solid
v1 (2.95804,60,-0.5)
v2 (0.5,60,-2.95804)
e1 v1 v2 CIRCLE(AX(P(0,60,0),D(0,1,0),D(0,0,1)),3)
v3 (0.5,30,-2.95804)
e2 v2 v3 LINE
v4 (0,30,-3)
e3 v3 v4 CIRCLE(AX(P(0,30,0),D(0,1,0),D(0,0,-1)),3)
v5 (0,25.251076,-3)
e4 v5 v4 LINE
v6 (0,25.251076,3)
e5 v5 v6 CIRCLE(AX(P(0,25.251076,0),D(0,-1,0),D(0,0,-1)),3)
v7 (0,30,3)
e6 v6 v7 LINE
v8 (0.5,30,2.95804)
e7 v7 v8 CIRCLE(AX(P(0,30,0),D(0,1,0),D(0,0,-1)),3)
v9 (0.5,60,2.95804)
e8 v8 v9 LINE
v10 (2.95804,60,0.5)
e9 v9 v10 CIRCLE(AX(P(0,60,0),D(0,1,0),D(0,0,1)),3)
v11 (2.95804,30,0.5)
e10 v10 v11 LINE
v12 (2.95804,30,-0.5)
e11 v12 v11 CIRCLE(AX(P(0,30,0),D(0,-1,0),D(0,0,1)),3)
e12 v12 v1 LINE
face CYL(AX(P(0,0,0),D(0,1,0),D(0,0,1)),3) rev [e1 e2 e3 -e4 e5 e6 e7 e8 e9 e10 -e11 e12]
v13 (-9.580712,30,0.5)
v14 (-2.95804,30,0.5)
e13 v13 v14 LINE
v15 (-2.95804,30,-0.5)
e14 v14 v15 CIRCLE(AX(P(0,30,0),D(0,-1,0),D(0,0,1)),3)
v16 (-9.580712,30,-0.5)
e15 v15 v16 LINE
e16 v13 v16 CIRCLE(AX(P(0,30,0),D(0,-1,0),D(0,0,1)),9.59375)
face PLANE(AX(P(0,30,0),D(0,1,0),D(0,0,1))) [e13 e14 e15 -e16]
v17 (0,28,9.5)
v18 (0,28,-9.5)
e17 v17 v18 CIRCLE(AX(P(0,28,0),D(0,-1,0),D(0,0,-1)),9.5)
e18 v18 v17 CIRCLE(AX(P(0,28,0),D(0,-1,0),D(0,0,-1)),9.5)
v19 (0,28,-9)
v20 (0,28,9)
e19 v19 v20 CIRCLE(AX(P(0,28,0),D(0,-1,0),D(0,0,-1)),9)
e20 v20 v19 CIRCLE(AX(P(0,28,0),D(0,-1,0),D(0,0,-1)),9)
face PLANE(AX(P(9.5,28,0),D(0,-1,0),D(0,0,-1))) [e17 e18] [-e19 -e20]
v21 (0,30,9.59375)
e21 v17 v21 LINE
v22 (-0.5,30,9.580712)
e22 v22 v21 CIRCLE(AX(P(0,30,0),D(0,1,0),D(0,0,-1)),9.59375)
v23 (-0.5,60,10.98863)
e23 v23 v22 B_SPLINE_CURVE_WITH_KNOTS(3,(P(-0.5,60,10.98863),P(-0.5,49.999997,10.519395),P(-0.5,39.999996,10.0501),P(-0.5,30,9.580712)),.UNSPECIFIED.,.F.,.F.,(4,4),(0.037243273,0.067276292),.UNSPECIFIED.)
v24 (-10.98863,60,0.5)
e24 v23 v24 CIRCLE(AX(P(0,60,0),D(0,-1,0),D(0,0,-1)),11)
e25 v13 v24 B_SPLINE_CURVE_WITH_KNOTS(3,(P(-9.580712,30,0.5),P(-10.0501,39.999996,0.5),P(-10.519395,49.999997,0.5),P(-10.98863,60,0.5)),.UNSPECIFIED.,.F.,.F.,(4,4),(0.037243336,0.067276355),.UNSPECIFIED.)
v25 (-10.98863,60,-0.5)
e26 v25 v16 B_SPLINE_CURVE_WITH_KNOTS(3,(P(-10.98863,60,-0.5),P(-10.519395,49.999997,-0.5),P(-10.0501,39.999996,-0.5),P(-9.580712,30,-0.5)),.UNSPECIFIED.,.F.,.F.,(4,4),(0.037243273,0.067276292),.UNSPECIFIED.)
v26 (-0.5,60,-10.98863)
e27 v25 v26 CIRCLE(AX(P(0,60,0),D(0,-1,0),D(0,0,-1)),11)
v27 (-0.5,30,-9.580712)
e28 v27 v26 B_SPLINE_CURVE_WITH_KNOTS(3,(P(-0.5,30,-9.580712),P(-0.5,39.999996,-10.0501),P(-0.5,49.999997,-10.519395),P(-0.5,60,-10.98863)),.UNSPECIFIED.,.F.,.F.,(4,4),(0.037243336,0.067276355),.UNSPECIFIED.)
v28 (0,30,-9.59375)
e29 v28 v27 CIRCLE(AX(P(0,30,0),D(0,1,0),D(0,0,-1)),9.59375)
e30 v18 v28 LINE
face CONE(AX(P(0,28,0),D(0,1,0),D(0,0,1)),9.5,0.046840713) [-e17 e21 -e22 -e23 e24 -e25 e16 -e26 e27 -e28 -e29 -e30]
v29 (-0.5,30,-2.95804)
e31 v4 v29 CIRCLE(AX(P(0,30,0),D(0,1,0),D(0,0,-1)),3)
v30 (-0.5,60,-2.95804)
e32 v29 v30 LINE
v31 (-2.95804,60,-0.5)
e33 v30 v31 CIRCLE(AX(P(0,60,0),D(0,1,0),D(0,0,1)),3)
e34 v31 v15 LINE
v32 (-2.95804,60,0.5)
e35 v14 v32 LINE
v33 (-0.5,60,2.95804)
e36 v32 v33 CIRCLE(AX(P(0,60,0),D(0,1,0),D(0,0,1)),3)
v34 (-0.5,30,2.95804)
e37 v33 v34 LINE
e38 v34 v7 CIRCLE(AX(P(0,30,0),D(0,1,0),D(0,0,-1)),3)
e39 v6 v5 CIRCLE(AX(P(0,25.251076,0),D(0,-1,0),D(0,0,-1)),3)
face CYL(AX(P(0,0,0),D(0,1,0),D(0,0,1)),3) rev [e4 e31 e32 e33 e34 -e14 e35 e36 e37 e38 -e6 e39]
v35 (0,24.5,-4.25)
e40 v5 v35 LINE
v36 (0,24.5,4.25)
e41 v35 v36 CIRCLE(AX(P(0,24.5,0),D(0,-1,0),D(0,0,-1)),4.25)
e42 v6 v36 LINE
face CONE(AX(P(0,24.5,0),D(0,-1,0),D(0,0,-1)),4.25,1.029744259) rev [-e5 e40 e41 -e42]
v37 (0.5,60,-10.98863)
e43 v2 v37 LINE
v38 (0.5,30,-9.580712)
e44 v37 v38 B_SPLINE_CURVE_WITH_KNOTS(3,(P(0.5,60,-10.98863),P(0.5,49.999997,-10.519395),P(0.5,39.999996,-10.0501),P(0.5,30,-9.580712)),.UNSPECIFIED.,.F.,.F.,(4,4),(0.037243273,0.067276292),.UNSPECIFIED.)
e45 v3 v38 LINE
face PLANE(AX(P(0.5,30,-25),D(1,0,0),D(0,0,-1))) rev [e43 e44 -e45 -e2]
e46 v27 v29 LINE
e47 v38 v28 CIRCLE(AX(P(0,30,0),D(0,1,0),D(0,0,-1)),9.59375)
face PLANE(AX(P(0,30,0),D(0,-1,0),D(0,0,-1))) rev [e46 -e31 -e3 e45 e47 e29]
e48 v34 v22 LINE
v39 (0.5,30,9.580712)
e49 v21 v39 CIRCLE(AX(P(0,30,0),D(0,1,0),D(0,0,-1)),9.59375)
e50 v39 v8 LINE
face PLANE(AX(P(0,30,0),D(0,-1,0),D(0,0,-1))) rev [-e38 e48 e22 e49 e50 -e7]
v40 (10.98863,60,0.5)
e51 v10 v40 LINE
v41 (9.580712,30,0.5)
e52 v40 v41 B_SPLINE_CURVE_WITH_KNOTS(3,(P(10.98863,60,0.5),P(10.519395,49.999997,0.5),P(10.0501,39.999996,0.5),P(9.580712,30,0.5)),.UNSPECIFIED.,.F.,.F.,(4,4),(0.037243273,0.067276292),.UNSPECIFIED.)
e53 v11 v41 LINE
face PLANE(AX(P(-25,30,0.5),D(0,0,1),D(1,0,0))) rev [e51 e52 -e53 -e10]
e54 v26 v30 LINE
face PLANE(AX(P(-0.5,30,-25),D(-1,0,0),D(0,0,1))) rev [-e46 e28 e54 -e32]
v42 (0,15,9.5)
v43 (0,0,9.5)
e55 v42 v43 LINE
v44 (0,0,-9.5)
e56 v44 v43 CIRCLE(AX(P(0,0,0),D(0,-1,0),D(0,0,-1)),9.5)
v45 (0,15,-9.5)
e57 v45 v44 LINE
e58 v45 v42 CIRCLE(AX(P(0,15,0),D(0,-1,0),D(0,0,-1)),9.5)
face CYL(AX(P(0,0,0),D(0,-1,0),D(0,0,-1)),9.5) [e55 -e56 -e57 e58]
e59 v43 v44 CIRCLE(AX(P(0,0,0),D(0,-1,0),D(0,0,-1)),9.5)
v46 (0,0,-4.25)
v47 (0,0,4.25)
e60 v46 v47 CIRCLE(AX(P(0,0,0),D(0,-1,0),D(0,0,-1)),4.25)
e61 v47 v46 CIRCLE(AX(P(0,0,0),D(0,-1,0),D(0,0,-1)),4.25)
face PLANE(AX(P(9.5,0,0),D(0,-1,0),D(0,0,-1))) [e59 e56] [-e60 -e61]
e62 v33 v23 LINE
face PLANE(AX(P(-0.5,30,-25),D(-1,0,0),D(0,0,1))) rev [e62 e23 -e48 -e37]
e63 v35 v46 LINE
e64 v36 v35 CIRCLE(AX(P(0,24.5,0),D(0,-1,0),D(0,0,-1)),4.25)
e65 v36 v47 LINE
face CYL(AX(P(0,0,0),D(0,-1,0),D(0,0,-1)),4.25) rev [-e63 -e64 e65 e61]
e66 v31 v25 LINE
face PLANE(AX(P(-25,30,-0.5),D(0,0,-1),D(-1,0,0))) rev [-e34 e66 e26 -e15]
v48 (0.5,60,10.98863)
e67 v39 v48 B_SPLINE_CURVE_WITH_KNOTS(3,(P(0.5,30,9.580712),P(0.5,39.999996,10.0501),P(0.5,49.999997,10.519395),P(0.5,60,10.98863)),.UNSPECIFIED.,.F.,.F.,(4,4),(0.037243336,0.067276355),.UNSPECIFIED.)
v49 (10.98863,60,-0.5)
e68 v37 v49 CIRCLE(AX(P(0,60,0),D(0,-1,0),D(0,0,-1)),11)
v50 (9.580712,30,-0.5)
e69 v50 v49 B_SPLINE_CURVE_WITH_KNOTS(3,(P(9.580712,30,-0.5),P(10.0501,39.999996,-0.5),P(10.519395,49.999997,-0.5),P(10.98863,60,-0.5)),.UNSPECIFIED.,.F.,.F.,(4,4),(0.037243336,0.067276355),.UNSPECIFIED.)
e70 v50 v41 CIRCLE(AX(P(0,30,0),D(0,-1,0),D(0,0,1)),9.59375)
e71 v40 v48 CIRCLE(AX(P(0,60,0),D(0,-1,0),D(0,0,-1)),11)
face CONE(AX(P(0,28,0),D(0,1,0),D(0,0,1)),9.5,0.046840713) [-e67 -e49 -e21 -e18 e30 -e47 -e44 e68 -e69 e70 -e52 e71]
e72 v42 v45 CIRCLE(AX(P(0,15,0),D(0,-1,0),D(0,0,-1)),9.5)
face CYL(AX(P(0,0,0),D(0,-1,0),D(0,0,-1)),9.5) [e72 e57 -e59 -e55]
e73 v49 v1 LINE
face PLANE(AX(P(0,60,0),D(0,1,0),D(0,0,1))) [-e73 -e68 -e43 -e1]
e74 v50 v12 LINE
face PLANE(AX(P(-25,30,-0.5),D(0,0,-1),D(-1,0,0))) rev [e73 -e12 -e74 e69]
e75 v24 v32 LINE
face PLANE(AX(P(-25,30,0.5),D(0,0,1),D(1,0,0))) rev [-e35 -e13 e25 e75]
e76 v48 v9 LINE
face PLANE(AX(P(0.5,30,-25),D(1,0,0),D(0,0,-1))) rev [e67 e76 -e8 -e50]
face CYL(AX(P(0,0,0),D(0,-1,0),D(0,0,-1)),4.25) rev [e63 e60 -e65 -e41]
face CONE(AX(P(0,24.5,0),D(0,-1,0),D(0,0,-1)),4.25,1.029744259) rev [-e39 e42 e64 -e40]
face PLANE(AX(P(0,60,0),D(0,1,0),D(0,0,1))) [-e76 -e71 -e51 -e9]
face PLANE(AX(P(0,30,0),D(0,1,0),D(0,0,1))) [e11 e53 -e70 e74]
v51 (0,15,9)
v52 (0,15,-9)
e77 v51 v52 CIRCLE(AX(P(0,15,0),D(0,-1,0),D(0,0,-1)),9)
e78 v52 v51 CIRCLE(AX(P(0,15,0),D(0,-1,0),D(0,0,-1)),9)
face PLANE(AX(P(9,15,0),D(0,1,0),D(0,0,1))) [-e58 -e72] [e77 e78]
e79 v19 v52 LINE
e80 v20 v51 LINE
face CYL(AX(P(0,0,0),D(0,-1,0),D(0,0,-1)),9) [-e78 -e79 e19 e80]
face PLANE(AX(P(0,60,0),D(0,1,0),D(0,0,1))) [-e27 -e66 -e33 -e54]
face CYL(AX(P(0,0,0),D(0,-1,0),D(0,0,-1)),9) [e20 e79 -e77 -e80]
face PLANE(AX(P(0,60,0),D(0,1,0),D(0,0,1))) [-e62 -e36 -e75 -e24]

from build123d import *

# Parameters (mm, degrees)
SKETCH_2_R              = 3
CUT_EXTRUDE_1_DEPTH     = 62.983868869
HOLE_WIZARD_M10_1_D     = 8.5
HOLE_WIZARD_M10_1_DEPTH = 24.5
HOLE_WIZARD_M10_1_TIP   = 2.553657631
SKETCH_4_W              = 50
SKETCH_4_H              = 1
CUT_EXTRUDE_2_DEPTH     = 30
SKETCH_5_W              = 1
SKETCH_5_H              = 50
CUT_EXTRUDE_3_DEPTH     = 30


with BuildPart() as part:
    # 草图1 → 旋转1 (revolve)
    with BuildSketch(Plane.XY, mode=Mode.PRIVATE) as revolve_1_sk:
        Polygon((0, 60), (11, 60), (9.5, 28), (9, 28), (9, 15), (9.5, 15), (9.5, 0), (0, 0), align=None)
    revolve(revolve_1_sk.sketch.rotate(Axis((0, 0, 0), (0, 1, 0)), 90), axis=Axis((0, 0, 0), (0, 1, 0)))

    # 草图2 → 切除-拉伸1 (cut, through all)
    with BuildSketch(Plane(origin=(0, 60, 0), x_dir=(1, 0, 0), z_dir=(0, 1, 0))):
        with Locations(Location((0, 0, 0), (0, 0, 270))):
            Circle(SKETCH_2_R)
    extrude(amount=-CUT_EXTRUDE_1_DEPTH, mode=Mode.SUBTRACT)

    # M10 螺纹孔1
    with Locations(Plane(origin=(0, 0, 0), x_dir=(0, 0, -1), z_dir=(0, -1, 0))):
        with Locations((0, 0)):
            Hole(HOLE_WIZARD_M10_1_D / 2, depth=HOLE_WIZARD_M10_1_DEPTH)
            with Locations((0, 0, -(HOLE_WIZARD_M10_1_DEPTH + HOLE_WIZARD_M10_1_TIP / 2))):  # 118° drill point
                Cone(0, HOLE_WIZARD_M10_1_D / 2, HOLE_WIZARD_M10_1_TIP, mode=Mode.SUBTRACT)

    # 草图4 → 切除-拉伸2 (cut)
    with BuildSketch(Plane(origin=(0, 60, 0), x_dir=(1, 0, 0), z_dir=(0, 1, 0))):
        Rectangle(SKETCH_4_W, SKETCH_4_H)
    extrude(amount=-CUT_EXTRUDE_2_DEPTH, mode=Mode.SUBTRACT)

    # 草图5 → 切除-拉伸3 (cut)
    with BuildSketch(Plane(origin=(0, 60, 0), x_dir=(1, 0, 0), z_dir=(0, 1, 0))):
        Rectangle(SKETCH_5_W, SKETCH_5_H)
    extrude(amount=-CUT_EXTRUDE_3_DEPTH, mode=Mode.SUBTRACT)


solid = part.part
